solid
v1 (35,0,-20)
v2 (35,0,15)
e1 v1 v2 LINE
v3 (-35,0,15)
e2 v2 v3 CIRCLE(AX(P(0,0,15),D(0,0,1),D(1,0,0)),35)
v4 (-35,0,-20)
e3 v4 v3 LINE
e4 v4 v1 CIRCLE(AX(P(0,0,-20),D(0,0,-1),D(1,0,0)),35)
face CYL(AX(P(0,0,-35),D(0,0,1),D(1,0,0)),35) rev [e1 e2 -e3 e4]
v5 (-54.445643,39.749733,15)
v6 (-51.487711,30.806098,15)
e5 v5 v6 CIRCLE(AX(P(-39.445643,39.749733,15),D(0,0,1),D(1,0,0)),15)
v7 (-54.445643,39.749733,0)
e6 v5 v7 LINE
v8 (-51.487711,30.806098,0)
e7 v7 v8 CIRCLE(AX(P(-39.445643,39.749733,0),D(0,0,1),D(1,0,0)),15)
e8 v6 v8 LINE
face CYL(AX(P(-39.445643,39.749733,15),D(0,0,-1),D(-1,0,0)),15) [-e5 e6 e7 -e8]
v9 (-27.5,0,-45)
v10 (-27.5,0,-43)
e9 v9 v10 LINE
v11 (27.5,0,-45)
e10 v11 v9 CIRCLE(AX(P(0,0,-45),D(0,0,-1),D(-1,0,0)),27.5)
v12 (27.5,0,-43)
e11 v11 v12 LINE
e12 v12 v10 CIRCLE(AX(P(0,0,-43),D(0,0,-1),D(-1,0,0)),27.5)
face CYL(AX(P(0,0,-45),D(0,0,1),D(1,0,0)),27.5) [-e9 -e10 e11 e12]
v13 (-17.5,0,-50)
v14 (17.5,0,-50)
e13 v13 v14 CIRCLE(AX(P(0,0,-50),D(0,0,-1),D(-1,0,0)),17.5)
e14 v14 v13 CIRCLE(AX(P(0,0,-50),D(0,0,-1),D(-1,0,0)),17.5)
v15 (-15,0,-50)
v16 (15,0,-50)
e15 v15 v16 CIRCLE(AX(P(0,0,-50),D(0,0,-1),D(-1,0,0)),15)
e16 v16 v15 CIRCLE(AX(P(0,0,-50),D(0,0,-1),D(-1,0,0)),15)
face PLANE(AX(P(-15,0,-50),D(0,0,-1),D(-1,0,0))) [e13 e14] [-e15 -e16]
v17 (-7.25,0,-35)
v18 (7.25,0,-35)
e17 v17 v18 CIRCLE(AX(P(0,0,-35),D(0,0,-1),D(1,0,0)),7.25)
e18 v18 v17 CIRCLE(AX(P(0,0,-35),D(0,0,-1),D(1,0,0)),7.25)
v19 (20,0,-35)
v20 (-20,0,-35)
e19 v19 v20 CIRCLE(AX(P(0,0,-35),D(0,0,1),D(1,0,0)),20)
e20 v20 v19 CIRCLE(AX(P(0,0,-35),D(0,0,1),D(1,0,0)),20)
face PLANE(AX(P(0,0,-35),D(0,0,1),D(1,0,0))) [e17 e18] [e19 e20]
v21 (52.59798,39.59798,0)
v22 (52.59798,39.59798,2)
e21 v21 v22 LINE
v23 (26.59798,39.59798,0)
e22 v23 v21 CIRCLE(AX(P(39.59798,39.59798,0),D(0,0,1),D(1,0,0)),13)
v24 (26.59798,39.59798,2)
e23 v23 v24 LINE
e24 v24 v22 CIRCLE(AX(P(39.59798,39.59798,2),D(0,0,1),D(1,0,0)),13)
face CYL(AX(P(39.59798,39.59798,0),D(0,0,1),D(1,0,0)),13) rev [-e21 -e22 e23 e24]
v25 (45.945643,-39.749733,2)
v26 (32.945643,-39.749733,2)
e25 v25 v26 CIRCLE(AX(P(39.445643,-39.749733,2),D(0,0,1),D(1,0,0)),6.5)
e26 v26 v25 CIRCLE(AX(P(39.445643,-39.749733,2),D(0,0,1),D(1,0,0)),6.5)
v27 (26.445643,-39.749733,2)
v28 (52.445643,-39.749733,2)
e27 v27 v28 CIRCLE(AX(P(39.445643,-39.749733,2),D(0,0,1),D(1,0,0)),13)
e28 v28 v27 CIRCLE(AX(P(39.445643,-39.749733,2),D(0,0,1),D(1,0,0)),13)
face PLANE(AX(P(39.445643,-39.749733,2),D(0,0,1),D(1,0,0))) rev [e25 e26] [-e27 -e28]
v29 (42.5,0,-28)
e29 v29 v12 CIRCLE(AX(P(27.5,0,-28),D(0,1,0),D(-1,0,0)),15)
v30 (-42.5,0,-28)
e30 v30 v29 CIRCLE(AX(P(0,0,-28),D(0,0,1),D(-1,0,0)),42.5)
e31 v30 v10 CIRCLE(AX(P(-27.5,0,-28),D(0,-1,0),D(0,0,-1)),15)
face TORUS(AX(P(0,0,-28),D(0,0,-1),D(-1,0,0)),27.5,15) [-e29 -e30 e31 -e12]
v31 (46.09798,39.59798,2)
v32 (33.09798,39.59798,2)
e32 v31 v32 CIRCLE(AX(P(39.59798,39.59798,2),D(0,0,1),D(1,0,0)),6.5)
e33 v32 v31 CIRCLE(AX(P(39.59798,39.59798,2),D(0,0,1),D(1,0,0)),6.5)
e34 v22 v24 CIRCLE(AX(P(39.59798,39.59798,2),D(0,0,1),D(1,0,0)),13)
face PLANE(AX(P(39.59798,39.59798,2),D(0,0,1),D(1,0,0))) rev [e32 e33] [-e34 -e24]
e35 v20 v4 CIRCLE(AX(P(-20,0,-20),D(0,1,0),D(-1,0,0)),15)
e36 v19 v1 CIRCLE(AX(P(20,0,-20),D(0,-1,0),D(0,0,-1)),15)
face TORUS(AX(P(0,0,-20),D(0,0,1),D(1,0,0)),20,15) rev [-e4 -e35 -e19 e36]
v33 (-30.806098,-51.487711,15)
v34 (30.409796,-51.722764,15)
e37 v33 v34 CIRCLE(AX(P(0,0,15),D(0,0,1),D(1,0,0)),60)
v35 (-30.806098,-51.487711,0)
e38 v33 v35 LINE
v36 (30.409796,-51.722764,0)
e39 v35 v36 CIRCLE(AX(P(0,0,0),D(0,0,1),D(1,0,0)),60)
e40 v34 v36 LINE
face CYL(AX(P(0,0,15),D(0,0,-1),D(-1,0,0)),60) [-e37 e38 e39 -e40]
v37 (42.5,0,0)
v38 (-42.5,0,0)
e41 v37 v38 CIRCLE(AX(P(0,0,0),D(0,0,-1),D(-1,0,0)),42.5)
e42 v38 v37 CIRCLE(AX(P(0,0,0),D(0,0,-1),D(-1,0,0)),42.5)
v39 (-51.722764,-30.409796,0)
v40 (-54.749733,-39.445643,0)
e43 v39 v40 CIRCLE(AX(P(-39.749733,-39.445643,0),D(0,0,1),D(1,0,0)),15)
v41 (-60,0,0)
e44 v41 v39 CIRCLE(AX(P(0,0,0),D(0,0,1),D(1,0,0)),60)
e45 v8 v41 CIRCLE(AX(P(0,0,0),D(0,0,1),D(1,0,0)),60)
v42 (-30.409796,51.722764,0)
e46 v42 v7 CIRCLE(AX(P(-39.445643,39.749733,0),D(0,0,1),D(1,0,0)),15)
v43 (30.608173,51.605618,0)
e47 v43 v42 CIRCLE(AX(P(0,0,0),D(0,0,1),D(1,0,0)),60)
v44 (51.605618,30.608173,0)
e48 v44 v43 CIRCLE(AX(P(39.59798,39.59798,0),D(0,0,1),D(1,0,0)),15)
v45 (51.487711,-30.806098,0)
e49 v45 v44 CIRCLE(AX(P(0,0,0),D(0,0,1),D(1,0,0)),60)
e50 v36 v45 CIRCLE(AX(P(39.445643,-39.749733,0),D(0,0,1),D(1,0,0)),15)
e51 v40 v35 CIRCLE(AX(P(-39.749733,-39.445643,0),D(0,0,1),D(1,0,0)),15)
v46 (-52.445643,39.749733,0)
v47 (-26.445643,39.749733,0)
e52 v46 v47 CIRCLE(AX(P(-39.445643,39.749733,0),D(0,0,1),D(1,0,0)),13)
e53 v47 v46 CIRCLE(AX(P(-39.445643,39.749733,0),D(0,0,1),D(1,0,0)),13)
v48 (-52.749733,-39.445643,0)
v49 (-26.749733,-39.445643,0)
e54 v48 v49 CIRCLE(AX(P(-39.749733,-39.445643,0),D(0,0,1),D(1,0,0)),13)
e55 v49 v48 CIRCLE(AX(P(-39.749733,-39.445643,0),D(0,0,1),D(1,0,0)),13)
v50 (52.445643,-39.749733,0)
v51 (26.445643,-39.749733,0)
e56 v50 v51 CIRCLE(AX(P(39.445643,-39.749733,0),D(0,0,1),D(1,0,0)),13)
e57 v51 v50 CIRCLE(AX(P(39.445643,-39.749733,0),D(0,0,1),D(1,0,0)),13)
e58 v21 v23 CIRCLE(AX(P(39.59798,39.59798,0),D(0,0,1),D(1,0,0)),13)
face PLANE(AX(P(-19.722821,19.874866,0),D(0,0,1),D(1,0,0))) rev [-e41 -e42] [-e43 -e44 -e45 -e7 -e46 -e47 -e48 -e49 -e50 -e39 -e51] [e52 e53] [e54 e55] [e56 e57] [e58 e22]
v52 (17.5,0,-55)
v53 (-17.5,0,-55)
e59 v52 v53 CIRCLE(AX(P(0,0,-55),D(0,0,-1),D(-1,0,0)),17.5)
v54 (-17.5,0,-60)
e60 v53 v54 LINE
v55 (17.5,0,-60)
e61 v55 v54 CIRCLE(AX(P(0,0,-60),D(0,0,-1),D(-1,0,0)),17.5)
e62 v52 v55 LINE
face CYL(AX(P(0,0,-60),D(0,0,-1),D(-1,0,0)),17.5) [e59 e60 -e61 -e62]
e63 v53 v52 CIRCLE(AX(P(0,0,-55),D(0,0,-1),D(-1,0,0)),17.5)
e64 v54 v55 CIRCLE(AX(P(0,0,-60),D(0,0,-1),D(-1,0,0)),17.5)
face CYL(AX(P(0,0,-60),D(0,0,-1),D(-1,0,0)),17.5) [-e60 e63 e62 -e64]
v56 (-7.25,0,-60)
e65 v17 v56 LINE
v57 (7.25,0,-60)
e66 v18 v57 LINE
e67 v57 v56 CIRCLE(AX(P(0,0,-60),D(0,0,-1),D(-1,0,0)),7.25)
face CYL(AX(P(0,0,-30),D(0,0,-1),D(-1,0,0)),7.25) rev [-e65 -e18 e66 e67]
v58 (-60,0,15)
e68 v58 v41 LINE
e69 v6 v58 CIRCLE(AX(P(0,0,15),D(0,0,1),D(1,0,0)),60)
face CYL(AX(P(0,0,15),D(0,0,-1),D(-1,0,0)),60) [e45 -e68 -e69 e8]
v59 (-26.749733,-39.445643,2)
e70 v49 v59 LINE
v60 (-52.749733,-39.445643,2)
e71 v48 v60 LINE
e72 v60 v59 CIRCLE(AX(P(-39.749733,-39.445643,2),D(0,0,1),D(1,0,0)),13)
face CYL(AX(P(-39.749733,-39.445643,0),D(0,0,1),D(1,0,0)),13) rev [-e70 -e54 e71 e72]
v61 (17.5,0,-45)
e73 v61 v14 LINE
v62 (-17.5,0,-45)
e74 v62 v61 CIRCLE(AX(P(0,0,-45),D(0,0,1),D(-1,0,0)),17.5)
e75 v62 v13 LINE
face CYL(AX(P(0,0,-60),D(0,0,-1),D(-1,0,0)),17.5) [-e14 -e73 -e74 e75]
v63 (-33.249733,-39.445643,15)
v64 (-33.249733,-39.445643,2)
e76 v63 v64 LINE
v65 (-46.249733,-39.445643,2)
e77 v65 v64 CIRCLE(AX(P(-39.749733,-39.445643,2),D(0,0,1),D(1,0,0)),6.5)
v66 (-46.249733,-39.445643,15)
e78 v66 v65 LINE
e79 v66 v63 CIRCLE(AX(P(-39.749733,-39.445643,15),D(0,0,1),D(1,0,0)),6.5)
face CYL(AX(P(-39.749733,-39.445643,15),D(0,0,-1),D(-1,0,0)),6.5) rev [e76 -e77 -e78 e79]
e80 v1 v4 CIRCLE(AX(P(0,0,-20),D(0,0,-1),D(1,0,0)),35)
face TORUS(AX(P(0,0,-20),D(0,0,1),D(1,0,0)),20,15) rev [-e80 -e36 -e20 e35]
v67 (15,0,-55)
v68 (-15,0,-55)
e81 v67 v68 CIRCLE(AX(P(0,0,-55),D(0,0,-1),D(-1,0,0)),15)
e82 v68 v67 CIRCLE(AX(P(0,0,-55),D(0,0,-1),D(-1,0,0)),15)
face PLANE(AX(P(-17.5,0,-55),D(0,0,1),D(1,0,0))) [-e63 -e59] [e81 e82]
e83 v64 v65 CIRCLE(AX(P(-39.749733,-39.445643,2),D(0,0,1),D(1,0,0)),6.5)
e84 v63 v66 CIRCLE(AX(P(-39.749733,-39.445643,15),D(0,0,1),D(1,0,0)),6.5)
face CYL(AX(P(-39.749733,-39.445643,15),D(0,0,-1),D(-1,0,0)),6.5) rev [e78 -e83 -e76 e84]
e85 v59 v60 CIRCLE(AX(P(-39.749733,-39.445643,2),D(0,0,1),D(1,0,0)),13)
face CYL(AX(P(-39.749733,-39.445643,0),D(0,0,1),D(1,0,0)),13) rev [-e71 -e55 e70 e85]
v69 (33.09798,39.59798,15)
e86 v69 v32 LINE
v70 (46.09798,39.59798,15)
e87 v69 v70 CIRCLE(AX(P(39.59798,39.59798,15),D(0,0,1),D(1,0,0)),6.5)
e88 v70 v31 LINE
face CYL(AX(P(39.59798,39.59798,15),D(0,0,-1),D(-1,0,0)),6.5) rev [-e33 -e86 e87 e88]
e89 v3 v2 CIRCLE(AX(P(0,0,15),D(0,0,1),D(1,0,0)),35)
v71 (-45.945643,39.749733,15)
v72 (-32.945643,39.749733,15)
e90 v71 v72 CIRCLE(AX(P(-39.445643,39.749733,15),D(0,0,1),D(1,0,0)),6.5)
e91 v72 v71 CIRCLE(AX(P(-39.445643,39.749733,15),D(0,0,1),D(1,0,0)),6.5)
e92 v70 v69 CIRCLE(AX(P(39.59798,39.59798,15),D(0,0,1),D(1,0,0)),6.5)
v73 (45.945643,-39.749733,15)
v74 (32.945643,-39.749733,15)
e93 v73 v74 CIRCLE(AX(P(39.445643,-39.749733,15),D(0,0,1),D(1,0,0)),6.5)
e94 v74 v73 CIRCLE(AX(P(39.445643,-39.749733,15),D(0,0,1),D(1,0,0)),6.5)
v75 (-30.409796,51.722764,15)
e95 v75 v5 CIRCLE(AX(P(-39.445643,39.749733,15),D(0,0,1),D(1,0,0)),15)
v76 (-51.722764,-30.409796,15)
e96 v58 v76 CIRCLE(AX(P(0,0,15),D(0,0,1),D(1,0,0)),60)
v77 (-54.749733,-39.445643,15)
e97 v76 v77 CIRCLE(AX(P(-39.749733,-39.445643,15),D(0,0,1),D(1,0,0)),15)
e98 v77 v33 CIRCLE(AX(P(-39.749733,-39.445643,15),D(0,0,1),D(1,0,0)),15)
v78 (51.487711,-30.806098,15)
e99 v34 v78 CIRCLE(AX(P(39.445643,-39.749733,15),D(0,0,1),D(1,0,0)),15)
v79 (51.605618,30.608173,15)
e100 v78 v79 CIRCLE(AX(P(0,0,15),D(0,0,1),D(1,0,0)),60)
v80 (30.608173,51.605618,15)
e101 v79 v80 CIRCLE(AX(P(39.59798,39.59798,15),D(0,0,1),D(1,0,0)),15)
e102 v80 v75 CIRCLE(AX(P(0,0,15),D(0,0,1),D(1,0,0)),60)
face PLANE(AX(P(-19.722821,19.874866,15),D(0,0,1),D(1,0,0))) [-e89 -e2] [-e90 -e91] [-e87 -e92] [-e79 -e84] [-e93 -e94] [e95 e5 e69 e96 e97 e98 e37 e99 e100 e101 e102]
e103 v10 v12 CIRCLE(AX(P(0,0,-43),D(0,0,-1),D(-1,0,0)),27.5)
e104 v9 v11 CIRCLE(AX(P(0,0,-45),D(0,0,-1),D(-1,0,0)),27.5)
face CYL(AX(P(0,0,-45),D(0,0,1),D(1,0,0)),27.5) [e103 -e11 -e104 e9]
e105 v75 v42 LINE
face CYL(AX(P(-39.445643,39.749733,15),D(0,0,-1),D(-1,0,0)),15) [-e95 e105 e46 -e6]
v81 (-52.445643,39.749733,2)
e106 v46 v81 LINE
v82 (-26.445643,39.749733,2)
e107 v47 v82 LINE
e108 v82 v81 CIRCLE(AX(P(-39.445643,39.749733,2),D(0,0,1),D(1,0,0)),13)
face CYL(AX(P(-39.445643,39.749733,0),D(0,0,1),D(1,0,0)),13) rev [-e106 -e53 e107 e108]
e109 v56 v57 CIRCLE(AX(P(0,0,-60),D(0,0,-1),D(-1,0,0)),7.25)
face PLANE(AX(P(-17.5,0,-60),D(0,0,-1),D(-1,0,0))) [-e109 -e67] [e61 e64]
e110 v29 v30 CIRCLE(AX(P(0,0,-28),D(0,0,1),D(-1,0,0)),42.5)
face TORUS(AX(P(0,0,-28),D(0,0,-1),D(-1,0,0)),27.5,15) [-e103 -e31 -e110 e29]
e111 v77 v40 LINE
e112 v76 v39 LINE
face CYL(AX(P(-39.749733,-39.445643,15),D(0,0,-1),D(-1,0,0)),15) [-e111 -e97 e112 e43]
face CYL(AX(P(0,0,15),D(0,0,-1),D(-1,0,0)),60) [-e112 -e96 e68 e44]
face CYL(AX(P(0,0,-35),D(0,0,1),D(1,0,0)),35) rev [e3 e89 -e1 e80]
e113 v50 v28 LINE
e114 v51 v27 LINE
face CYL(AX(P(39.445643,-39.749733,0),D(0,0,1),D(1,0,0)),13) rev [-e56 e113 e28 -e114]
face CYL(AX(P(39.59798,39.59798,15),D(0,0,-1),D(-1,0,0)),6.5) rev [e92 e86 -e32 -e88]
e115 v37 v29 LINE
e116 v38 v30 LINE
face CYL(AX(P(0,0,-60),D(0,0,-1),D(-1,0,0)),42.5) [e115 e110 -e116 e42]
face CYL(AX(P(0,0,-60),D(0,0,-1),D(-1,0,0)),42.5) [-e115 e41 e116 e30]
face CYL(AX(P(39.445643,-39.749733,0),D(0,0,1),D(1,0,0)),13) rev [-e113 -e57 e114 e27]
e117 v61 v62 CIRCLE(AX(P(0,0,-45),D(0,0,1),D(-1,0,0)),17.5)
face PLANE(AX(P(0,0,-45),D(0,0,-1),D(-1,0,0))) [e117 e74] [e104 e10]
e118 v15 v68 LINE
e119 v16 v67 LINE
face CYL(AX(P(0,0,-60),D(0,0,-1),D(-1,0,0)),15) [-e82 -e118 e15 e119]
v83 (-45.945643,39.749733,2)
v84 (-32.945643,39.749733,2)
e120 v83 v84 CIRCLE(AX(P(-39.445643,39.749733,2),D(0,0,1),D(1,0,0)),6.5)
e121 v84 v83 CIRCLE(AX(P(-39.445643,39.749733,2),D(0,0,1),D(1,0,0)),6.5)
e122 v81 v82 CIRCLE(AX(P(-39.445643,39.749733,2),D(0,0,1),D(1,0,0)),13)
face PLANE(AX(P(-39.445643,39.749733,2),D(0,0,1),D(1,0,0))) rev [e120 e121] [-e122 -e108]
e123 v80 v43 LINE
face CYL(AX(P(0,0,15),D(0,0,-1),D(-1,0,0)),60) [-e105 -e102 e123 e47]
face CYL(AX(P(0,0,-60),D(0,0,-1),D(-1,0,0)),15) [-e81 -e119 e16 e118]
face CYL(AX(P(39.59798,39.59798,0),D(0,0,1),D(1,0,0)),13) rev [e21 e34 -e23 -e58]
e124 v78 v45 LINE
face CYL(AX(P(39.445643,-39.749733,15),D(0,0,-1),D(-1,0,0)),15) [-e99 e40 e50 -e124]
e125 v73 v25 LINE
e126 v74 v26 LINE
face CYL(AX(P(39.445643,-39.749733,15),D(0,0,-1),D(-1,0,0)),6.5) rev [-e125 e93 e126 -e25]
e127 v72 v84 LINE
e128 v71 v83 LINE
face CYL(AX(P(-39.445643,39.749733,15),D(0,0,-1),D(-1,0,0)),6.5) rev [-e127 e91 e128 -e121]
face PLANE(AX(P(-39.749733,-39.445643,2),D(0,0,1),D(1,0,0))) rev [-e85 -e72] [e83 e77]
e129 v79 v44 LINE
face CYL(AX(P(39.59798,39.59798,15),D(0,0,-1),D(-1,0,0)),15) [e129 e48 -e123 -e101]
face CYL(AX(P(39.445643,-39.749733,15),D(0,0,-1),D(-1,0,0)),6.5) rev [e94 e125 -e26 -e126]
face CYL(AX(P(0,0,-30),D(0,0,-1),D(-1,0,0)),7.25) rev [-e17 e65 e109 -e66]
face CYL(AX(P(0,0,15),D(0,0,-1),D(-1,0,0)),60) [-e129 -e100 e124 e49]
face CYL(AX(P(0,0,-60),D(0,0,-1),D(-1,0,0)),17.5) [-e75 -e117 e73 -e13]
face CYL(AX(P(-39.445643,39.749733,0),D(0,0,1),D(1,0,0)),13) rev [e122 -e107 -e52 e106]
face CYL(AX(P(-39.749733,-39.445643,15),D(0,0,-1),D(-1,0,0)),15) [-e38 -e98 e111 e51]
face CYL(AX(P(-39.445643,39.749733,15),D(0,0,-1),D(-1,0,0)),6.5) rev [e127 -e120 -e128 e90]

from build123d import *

# Parameters (mm, degrees)
SKETCH1_R           = 6.5
BOSS_EXTRUDE1_DEPTH = 15
CUT_EXTRUDE1_START  = -13
SKETCH2_R           = 13
CUT_EXTRUDE1_DEPTH  = 2
FILLET1_R           = 15
SKETCH4_R           = 27.5
BOSS_EXTRUDE2_DEPTH = 2
SKETCH5_R           = 7.25
CUT_EXTRUDE2_DEPTH  = 30
SKETCH6_R           = 35
CUT_EXTRUDE3_DEPTH  = 50
FILLET2_R           = 15


with BuildPart() as part:
    # Sketch1 → Boss-Extrude1 (new body)
    with BuildSketch(Plane.XY):
        with BuildLine():
            ThreePointArc((30.608172596, 51.605617624), (0.11519166, 59.999889424), (-30.409796101, 51.722763858))
            ThreePointArc((-30.409796101, 51.722763858), (-50.011440089, 50.39698265), (-51.487710544, 30.806097821))
            ThreePointArc((-51.487710544, 30.806097821), (-59.999557696, 0.230382895), (-51.722763858, -30.409796101))
            ThreePointArc((-51.722763858, -30.409796101), (-50.39698265, -50.011440089), (-30.806097821, -51.487710544))
            ThreePointArc((-30.806097821, -51.487710544), (-0.230382895, -59.999557696), (30.409796101, -51.722763858))
            ThreePointArc((30.409796101, -51.722763858), (50.011440089, -50.39698265), (51.487710544, -30.806097821))
            ThreePointArc((51.487710544, -30.806097821), (59.999889424, -0.11519166), (51.605617624, 30.608172596))
            ThreePointArc((51.605617624, 30.608172596), (50.204581464, 50.204581464), (30.608172596, 51.605617624))
        make_face()
        with Locations((39.597979746, 39.597979746)):
            Circle(SKETCH1_R, mode=Mode.SUBTRACT)
        with Locations((-39.445642887, 39.749732794)):
            Circle(SKETCH1_R, mode=Mode.SUBTRACT)
        with Locations((-39.749732794, -39.445642887)):
            Circle(SKETCH1_R, mode=Mode.SUBTRACT)
        with Locations((39.445642887, -39.749732794)):
            Circle(SKETCH1_R, mode=Mode.SUBTRACT)
    extrude(amount=BOSS_EXTRUDE1_DEPTH)

    # Sketch2 → Cut-Extrude1 (cut)
    with BuildSketch(Plane.XY.offset(15).offset(CUT_EXTRUDE1_START)):
        with Locations((-39.445642887, 39.749732794)):
            Circle(SKETCH2_R)
        with Locations((39.597979746, 39.597979746)):
            Circle(SKETCH2_R)
        with Locations((39.445642887, -39.749732794)):
            Circle(SKETCH2_R)
        with Locations((-39.749732794, -39.445642887)):
            Circle(SKETCH2_R)
    extrude(amount=-CUT_EXTRUDE1_DEPTH, mode=Mode.SUBTRACT)

    # Sketch3 → Revolve1 (revolve)
    with BuildSketch(Plane(origin=(0, 0, 0), x_dir=(1, 0, 0), z_dir=(0, 1, 0))):
        Polygon((-42.5, 0), (-42.5, 43), (-17.5, 43), (-17.5, 50), (-15, 50), (-15, 55), (-17.5, 55), (-17.5, 60), (0, 60), (0, 0), align=None)
    revolve(axis=Axis((0, 0, -60), (0, 0, 1)))

    # Fillet1
    fillet1_edges = [part.edges().sort_by_distance(p)[0] for p in [
        (42.5, 0, -43),
    ]]
    fillet(fillet1_edges, radius=FILLET1_R)

    # Sketch4 → Boss-Extrude2 (add)
    with BuildSketch(Plane(origin=(0, 0, -43), x_dir=(-1, 0, 0), z_dir=(0, 0, -1))):
        Circle(SKETCH4_R)
    extrude(amount=BOSS_EXTRUDE2_DEPTH)

    # Sketch5 → Cut-Extrude2 (cut)
    with BuildSketch(Plane(origin=(0, 0, -60), x_dir=(-1, 0, 0), z_dir=(0, 0, -1))):
        Circle(SKETCH5_R)
    extrude(amount=-CUT_EXTRUDE2_DEPTH, mode=Mode.SUBTRACT)

    # Sketch6 → Cut-Extrude3 (cut)
    with BuildSketch(Plane.XY.offset(15)):
        Circle(SKETCH6_R)
    extrude(amount=-CUT_EXTRUDE3_DEPTH, mode=Mode.SUBTRACT)

    # Fillet2
    fillet2_edges = [part.edges().sort_by_distance(p)[0] for p in [
        (-35, 0, -35),
    ]]
    fillet(fillet2_edges, radius=FILLET2_R)


solid = part.part
